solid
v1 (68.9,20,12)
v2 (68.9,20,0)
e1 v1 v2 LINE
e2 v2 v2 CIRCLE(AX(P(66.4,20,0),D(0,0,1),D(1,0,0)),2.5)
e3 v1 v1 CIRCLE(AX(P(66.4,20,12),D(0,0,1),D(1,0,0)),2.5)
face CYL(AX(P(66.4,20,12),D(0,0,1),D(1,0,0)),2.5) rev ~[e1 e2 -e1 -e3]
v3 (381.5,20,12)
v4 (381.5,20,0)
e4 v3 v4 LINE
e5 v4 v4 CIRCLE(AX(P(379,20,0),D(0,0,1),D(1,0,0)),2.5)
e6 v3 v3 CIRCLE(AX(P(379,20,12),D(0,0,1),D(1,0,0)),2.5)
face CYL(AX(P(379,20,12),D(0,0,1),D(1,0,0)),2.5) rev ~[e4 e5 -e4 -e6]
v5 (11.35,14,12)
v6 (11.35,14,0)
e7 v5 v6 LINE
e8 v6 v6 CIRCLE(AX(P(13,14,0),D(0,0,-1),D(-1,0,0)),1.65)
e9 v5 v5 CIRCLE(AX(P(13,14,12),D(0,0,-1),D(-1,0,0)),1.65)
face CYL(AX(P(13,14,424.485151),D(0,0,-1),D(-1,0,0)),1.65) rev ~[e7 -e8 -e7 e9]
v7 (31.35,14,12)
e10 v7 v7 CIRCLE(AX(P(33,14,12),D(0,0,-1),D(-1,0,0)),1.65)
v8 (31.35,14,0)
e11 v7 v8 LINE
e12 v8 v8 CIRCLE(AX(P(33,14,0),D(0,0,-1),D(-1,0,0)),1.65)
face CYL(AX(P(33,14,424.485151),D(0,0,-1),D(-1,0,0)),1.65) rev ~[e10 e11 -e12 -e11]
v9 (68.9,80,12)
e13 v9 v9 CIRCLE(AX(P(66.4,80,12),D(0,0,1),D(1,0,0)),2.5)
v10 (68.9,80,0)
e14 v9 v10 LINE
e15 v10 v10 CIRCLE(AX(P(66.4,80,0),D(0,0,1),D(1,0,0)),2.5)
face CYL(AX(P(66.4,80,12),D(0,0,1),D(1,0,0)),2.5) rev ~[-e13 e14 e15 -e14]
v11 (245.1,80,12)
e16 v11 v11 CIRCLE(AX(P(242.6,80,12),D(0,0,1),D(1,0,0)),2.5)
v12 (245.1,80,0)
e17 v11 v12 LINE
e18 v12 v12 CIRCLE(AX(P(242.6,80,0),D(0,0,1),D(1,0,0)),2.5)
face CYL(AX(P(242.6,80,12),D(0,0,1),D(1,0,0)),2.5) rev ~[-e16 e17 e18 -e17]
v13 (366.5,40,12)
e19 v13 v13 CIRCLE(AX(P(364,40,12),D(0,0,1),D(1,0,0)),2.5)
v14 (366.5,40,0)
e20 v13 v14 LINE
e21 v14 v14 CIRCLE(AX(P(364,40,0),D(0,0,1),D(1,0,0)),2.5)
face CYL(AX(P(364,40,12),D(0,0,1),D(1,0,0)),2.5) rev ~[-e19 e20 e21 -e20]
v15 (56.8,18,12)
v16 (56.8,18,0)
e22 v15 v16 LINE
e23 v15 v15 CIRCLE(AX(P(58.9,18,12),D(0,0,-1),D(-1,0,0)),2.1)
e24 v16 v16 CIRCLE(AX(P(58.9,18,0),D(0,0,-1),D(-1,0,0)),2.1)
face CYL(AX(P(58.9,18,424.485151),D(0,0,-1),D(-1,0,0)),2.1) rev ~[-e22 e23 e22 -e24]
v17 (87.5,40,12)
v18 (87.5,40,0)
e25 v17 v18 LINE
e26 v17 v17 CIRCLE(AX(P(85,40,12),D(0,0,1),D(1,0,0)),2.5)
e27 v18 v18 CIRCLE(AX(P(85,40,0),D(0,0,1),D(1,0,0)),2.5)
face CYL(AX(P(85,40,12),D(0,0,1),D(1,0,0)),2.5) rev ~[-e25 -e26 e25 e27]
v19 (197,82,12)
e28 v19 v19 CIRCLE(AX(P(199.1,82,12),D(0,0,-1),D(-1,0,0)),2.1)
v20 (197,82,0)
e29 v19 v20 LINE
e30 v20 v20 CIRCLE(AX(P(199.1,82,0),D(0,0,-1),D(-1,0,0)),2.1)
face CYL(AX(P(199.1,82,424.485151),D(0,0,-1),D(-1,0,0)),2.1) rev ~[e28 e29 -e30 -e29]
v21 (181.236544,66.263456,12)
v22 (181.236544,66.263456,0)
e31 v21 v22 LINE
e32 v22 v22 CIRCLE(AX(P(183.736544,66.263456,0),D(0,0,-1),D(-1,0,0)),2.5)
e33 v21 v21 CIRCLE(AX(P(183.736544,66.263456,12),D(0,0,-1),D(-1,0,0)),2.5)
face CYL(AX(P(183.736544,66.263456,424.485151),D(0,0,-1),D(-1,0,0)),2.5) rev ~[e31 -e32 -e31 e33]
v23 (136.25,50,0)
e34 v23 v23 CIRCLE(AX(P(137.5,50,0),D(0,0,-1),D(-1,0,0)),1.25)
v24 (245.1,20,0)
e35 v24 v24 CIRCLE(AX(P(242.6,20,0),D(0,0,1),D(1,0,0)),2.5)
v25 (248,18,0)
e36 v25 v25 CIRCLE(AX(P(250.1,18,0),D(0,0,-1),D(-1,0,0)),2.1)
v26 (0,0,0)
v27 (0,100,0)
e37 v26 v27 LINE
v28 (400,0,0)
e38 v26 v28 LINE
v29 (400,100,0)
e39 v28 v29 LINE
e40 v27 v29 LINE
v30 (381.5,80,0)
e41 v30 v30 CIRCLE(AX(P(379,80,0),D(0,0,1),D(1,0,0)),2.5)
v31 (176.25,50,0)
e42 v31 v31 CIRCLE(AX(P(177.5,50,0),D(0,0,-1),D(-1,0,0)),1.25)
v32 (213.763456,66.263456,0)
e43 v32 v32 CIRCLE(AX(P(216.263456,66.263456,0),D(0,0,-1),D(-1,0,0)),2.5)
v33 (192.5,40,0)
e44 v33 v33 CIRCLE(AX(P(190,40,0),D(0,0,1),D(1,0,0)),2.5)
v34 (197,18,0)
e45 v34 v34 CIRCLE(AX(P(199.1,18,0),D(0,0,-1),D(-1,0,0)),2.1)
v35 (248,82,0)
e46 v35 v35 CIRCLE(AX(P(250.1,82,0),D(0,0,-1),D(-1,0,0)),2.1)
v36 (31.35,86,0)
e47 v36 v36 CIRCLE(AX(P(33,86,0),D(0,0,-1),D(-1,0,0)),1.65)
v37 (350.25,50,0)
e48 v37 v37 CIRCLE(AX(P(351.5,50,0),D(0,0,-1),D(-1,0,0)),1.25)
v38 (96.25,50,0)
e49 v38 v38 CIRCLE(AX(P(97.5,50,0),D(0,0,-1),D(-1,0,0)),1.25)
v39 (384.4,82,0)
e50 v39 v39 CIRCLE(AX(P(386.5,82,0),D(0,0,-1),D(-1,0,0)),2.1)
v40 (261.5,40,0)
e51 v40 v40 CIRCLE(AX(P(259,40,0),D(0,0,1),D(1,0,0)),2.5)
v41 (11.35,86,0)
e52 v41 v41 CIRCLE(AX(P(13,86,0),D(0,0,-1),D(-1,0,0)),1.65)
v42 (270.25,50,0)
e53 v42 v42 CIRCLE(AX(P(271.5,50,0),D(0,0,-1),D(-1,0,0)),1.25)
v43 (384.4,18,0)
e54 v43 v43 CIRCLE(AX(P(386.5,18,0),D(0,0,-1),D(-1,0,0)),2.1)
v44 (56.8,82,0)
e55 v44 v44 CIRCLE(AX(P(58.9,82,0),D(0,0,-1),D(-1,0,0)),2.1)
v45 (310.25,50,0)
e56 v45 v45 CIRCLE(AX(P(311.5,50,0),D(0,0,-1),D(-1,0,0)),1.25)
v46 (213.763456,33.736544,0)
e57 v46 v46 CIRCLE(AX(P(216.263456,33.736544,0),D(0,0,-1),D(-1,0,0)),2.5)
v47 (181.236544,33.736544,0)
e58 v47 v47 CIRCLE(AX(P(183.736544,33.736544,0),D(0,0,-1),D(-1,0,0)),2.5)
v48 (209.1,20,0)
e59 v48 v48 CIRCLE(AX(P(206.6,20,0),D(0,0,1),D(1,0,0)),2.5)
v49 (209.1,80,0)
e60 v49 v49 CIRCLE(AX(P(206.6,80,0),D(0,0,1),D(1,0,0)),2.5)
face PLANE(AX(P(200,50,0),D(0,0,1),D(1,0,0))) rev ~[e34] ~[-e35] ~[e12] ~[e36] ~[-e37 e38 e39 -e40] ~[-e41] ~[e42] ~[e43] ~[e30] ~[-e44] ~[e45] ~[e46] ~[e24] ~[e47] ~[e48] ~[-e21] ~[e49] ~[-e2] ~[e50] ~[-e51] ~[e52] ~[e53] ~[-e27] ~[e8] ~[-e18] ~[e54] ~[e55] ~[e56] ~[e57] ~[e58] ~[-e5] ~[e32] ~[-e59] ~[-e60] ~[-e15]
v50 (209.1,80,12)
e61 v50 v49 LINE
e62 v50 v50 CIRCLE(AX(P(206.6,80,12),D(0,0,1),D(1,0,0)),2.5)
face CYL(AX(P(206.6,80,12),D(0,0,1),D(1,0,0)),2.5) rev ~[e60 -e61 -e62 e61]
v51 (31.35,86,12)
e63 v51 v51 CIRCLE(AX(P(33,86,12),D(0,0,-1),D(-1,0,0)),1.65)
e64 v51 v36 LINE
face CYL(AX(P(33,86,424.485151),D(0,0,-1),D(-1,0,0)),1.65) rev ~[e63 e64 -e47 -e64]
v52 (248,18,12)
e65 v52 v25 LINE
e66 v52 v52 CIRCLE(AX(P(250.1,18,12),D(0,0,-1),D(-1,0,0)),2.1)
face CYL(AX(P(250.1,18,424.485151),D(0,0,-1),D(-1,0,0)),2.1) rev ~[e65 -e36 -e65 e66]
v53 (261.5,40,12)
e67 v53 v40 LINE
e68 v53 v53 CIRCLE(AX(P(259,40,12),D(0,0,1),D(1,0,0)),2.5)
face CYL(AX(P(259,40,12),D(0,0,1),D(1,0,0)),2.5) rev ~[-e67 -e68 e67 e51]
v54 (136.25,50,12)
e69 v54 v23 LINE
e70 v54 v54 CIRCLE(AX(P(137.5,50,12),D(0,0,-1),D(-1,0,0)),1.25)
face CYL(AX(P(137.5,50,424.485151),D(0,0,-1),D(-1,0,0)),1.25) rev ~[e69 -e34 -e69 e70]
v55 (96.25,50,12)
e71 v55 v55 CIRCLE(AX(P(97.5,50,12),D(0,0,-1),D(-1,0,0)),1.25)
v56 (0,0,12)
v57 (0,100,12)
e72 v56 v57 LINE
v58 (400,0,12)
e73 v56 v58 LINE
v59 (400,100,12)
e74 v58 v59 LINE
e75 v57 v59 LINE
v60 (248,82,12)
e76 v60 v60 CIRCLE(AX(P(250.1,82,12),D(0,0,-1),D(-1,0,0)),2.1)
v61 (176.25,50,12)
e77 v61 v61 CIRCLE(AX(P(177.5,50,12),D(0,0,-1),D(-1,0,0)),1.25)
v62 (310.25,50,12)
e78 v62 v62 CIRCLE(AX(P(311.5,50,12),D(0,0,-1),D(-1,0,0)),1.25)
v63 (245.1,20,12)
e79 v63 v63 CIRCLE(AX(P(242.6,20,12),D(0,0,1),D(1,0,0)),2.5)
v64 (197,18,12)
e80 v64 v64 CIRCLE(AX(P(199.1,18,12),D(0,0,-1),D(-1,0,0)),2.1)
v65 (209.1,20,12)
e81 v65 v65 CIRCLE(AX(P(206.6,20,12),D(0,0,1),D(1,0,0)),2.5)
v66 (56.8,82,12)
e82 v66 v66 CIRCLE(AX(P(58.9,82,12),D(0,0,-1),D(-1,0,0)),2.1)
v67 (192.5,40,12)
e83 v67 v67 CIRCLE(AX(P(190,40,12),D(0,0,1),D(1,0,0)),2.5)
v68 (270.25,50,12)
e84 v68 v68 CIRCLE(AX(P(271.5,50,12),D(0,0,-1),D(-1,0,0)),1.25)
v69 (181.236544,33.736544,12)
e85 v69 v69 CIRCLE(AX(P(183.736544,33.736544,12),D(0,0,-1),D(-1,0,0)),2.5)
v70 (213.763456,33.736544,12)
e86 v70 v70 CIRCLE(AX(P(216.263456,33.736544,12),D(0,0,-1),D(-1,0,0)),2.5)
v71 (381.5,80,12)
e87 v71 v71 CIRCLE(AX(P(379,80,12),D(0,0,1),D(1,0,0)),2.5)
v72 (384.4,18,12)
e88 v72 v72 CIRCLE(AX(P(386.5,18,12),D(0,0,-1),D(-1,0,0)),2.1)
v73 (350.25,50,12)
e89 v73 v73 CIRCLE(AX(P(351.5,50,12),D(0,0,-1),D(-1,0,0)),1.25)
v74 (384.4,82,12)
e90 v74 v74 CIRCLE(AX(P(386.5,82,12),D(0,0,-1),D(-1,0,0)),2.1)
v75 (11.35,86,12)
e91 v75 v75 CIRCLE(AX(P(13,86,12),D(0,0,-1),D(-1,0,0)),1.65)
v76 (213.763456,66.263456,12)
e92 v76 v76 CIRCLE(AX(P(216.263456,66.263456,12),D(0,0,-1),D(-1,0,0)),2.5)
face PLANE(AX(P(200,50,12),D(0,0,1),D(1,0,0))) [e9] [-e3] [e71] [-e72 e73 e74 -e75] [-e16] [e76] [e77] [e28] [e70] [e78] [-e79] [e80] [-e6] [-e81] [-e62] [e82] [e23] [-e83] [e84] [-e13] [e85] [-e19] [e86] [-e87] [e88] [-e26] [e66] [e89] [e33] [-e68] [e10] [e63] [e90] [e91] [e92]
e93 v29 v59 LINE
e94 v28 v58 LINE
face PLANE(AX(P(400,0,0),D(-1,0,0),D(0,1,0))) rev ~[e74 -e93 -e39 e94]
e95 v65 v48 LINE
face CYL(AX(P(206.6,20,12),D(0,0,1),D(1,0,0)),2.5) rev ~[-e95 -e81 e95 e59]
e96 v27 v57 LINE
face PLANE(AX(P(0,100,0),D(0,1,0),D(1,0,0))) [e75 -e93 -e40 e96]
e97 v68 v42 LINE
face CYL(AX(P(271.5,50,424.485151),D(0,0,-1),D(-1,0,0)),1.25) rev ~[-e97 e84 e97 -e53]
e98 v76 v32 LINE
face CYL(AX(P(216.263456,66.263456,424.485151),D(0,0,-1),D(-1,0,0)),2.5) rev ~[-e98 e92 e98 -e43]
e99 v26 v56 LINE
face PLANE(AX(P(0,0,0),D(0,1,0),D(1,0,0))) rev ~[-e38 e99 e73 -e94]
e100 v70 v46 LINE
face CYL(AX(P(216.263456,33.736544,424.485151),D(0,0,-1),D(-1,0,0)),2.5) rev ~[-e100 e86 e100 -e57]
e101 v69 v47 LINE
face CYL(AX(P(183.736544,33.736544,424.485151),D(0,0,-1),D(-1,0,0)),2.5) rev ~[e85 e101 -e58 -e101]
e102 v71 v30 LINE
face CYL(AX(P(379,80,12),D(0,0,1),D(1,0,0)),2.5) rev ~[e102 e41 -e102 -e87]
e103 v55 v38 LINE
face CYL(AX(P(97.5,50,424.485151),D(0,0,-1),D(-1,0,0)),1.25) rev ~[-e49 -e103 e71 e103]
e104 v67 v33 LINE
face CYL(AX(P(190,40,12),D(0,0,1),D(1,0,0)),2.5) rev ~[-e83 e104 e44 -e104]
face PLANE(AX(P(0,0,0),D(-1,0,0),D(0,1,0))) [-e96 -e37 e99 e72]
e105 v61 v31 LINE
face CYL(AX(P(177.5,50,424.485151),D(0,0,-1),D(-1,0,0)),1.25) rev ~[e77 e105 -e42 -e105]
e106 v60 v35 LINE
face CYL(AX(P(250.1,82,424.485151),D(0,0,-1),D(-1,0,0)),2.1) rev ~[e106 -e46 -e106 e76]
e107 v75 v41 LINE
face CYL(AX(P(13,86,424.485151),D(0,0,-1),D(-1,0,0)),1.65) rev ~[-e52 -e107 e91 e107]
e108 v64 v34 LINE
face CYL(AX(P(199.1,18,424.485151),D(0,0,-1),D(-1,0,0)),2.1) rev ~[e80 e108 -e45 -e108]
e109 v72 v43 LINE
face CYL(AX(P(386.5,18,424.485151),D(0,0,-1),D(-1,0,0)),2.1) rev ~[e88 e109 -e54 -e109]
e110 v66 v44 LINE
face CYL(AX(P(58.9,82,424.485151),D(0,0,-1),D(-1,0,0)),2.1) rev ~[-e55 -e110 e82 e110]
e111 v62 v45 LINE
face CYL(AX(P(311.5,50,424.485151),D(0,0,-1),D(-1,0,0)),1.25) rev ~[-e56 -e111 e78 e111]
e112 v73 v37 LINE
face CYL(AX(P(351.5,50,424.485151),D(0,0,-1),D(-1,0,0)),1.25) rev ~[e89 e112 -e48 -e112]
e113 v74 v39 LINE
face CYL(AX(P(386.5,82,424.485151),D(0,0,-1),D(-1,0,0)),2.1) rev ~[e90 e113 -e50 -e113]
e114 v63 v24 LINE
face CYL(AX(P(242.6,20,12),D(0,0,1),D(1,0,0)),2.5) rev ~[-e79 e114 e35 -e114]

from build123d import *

# Parameters (mm, degrees)
SKETCH1_W           = 400
SKETCH1_H           = 100
BOSS_EXTRUDE1_DEPTH = 12
M4_TAPPED_HOLE1_D   = 3.3
M5_TAPPED_HOLE1_D   = 4.2
SKETCH6_R           = 2.5
CUT_EXTRUDE1_DEPTH  = 413.485151248
M6_TAPPED_HOLE1_D   = 5
M3_TAPPED_HOLE1_D   = 2.5


with BuildPart() as part:
    # Sketch1 → Boss-Extrude1 (new body)
    with BuildSketch(Plane.XY):
        with Locations((200, 50)):
            Rectangle(SKETCH1_W, SKETCH1_H)
    extrude(amount=BOSS_EXTRUDE1_DEPTH)

    # M4 Tapped Hole1 (through all)
    with Locations(Plane.XY.offset(12)):
        with Locations((13, 14), (13, 86), (33, 86), (33, 14)):
            Hole(M4_TAPPED_HOLE1_D / 2)

    # M5 Tapped Hole1 (through all)
    with Locations(Plane.XY.offset(12)):
        with Locations((58.9, 82), (58.9, 18), (199.1, 82), (199.1, 18), (250.1, 18), (250.1, 82), (386.5, 82), (386.5, 18)):
            Hole(M5_TAPPED_HOLE1_D / 2)

    # Sketch6 → Cut-Extrude1 (cut, through all)
    with BuildSketch(Plane.XY.offset(12)):
        with Locations((66.4, 80)):
            Circle(SKETCH6_R)
        with Locations((66.4, 20)):
            Circle(SKETCH6_R)
        with Locations((206.6, 80)):
            Circle(SKETCH6_R)
        with Locations((206.6, 20)):
            Circle(SKETCH6_R)
        with Locations((242.6, 20)):
            Circle(SKETCH6_R)
        with Locations((242.6, 80)):
            Circle(SKETCH6_R)
        with Locations((379, 80)):
            Circle(SKETCH6_R)
        with Locations((379, 20)):
            Circle(SKETCH6_R)
        with Locations((85, 40)):
            Circle(SKETCH6_R)
        with Locations((190, 40)):
            Circle(SKETCH6_R)
        with Locations((259, 40)):
            Circle(SKETCH6_R)
        with Locations((364, 40)):
            Circle(SKETCH6_R)
    extrude(amount=-CUT_EXTRUDE1_DEPTH, mode=Mode.SUBTRACT)

    # M6 Tapped Hole1 (through all)
    with Locations(Plane.XY.offset(12)):
        with Locations((183.736544033, 66.263455967), (216.263455967, 66.263455967), (216.263455967, 33.736544033), (183.736544033, 33.736544033)):
            Hole(M6_TAPPED_HOLE1_D / 2)

    # M3 Tapped Hole1 (through all)
    with Locations(Plane.XY.offset(12)):
        with Locations((97.5, 50), (137.5, 50), (177.5, 50), (271.5, 50), (311.5, 50), (351.5, 50)):
            Hole(M3_TAPPED_HOLE1_D / 2)


solid = part.part
